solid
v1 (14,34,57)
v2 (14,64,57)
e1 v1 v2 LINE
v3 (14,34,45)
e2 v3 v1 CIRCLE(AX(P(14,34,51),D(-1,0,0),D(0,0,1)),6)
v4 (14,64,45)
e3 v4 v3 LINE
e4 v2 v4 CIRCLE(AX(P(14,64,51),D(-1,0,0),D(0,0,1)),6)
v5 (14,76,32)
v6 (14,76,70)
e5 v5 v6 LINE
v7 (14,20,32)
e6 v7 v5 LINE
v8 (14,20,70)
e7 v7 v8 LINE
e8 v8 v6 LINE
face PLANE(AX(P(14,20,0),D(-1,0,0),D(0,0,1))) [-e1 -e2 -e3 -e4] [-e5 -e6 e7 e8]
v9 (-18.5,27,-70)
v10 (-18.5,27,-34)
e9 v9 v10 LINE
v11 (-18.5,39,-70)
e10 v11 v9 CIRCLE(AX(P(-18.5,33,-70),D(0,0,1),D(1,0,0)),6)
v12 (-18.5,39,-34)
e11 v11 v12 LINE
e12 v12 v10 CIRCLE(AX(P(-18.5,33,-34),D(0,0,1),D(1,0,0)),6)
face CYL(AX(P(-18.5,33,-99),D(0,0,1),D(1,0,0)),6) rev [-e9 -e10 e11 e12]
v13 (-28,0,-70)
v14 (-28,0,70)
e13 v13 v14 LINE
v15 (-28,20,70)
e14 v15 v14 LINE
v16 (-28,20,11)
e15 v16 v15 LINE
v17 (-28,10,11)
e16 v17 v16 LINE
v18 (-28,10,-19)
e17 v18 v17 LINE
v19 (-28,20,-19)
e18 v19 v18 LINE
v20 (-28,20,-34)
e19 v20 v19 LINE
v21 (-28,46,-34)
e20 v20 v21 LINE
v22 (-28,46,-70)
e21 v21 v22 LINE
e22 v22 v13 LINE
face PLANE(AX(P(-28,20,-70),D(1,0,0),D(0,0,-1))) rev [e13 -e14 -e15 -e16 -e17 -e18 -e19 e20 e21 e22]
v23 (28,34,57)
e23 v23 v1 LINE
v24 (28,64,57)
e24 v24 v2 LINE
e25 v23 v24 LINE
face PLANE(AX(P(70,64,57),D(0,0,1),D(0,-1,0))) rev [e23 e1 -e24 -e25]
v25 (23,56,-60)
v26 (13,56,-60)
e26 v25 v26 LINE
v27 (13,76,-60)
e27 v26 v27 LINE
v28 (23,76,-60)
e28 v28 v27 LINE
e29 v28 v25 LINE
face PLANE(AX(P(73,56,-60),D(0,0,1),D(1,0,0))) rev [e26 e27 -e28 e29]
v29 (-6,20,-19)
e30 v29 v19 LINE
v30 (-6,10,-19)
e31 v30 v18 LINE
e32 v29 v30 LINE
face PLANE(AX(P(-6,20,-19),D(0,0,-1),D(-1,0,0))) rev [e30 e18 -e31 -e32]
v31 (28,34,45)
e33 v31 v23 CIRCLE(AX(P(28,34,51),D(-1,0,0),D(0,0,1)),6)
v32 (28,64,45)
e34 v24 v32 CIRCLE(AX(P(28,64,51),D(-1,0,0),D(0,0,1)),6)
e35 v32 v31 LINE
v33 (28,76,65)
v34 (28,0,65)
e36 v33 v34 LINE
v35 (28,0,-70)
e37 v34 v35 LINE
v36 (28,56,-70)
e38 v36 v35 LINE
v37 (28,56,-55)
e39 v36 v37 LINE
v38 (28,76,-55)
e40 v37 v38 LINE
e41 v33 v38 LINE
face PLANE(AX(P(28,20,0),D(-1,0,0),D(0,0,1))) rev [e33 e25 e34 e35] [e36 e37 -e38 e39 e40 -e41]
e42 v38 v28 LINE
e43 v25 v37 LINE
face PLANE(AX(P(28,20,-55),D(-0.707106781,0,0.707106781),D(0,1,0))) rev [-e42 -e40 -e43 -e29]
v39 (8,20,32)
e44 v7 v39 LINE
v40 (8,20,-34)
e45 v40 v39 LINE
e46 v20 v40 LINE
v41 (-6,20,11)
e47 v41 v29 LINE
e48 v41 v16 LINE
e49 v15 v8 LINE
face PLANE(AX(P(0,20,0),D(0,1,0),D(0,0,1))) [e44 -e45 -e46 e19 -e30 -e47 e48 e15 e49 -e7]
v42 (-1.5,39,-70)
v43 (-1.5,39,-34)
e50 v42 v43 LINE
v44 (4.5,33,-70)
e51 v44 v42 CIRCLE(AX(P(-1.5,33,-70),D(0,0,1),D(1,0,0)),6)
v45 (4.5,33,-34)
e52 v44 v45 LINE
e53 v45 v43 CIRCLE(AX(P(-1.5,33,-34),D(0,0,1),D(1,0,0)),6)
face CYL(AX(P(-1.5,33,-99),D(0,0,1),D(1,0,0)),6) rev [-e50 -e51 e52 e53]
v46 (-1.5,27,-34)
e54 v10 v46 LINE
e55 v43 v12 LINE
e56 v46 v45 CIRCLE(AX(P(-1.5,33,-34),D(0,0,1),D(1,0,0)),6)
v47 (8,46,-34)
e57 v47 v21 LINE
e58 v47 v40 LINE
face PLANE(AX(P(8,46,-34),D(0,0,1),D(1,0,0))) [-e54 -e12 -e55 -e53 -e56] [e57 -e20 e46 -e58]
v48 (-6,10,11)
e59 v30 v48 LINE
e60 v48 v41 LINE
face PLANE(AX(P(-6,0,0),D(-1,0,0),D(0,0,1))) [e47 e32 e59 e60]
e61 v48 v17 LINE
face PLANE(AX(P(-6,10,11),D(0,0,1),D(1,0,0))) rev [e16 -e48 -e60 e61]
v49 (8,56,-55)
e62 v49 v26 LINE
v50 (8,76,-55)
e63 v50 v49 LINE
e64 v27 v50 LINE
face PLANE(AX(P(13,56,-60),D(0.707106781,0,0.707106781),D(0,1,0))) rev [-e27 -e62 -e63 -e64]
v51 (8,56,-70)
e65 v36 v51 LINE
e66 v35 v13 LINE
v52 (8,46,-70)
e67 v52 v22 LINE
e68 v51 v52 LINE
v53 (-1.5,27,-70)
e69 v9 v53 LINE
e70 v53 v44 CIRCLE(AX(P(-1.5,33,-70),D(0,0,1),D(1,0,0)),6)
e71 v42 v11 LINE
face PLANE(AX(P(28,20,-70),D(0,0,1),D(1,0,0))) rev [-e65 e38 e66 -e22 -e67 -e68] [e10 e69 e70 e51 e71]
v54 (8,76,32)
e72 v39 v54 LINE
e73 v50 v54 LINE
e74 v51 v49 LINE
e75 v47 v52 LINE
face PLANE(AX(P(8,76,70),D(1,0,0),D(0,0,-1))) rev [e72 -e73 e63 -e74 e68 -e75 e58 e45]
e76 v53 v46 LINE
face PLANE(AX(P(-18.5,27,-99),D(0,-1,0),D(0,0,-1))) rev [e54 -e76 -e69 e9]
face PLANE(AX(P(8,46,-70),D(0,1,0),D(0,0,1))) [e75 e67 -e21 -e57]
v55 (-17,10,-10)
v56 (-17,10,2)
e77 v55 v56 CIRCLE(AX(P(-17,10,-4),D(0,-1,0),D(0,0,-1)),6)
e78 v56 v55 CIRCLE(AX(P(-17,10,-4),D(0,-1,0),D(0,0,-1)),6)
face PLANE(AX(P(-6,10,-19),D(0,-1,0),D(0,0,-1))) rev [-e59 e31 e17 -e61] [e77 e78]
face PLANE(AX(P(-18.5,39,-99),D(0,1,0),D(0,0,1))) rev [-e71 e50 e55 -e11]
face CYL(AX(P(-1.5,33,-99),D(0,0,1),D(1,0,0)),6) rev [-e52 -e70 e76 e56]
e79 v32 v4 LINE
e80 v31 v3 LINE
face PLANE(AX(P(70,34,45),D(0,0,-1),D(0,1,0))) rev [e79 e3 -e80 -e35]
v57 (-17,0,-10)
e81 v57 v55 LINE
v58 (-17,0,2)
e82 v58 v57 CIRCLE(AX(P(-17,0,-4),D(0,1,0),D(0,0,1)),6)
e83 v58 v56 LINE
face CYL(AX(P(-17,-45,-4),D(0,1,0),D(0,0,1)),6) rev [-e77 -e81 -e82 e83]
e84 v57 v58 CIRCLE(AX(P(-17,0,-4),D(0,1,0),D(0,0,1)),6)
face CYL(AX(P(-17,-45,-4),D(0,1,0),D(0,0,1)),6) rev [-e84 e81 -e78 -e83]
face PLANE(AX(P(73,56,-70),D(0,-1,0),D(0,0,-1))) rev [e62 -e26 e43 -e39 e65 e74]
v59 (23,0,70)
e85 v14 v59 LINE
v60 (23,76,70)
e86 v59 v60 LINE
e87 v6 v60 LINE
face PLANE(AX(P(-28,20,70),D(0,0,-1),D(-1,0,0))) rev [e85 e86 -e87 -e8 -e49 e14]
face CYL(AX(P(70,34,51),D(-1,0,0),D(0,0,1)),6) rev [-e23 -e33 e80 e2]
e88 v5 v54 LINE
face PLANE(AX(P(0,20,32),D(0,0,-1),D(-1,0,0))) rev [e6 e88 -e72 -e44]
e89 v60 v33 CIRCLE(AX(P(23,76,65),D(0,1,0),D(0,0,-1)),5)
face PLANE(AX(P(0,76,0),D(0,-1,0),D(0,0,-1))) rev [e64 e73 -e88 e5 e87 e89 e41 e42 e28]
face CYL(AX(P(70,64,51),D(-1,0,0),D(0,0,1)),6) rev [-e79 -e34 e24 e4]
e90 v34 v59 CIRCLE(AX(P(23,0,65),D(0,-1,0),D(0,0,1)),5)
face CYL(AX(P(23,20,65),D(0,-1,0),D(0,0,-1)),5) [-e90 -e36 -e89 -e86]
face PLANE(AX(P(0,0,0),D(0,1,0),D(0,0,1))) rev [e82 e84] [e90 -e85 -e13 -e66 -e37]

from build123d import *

# Parameters (mm, degrees)
BASE_PLATE_DEPTH            = 20
UPRIGHT_WALL_SKETCH_W       = 20
UPRIGHT_WALL_SKETCH_H       = 140
UPRIGHT_WALL_DEPTH          = 56
WALL_PROFILE_CUT_SKETCH_W   = 6
WALL_PROFILE_CUT_SKETCH_H   = 38
WALL_PROFILE_CUT_DEPTH      = 56
WALL_SLOT_DEPTH             = 56
TOP_RIDGE_SKETCH_W          = 36
TOP_RIDGE_SKETCH_H          = 46
TOP_RIDGE_DEPTH             = 36
WALL_NOTCH_SKETCH_W         = 30
WALL_NOTCH_SKETCH_H         = 10
WALL_NOTCH_DEPTH            = 22
ROUND_CUT_SKETCH_R          = 6
ROUND_CUT_DEPTH             = 65
STEP_CUT_SKETCH_W           = 10
STEP_CUT_SKETCH_H           = 20
STEP_CUT_DEPTH              = 65
STEP_CHAMFER_5MM_SIZE       = 5
BASE_EDGE_CHAMFER_5X45_SIZE = 5
CORNER_FILLET_R5_R          = 5
RIDGE_SLOT_DEPTH            = 65


with BuildPart() as part:
    # Base Plate Sketch → Base Plate (new body)
    with BuildSketch(Plane(origin=(0, 0, 0), x_dir=(1, 0, 0), z_dir=(0, 1, 0))):
        Polygon((28, 0), (28, 70), (-28, 70), (-28, -70), (28, -70), align=None)
    extrude(amount=BASE_PLATE_DEPTH)

    # Upright Wall Sketch → Upright Wall (add)
    with BuildSketch(Plane(origin=(0, 20, 0), x_dir=(1, 0, 0), z_dir=(0, 1, 0))):
        with Locations((18, 0)):
            Rectangle(UPRIGHT_WALL_SKETCH_W, UPRIGHT_WALL_SKETCH_H)
    extrude(amount=UPRIGHT_WALL_DEPTH)

    # Wall Profile Cut Sketch → Wall Profile Cut (cut)
    with BuildSketch(Plane(origin=(0, 76, 0), x_dir=(1, 0, 0), z_dir=(0, 1, 0))):
        with Locations((11, -51)):
            Rectangle(WALL_PROFILE_CUT_SKETCH_W, WALL_PROFILE_CUT_SKETCH_H)
    extrude(amount=-WALL_PROFILE_CUT_DEPTH, mode=Mode.SUBTRACT)

    # Wall Slot Sketch → Wall Slot (cut)
    with BuildSketch(Plane.ZY.offset(-14)):
        with BuildLine():
            Line((57, 64), (57, 34))
            ThreePointArc((57, 34), (51, 28), (45, 34))
            Line((45, 34), (45, 64))
            ThreePointArc((45, 64), (51, 70), (57, 64))
        make_face()
    extrude(amount=-WALL_SLOT_DEPTH, mode=Mode.SUBTRACT)

    # Top Ridge Sketch → Top Ridge (add)
    with BuildSketch(Plane.ZY.offset(28)):
        with Locations((-52, 23)):
            Rectangle(TOP_RIDGE_SKETCH_W, TOP_RIDGE_SKETCH_H)
    extrude(amount=-TOP_RIDGE_DEPTH)

    # Wall Notch Sketch → Wall Notch (cut)
    with BuildSketch(Plane.ZY.offset(28)):
        with Locations((-4, 15)):
            Rectangle(WALL_NOTCH_SKETCH_W, WALL_NOTCH_SKETCH_H)
    extrude(amount=-WALL_NOTCH_DEPTH, mode=Mode.SUBTRACT)

    # Round Cut Sketch → Round Cut (cut)
    with BuildSketch(Plane(origin=(0, 20, 0), x_dir=(1, 0, 0), z_dir=(0, 1, 0))):
        with Locations(Location((-17, 4, 0), (0, 0, 270))):
            Circle(ROUND_CUT_SKETCH_R)
    extrude(amount=-ROUND_CUT_DEPTH, mode=Mode.SUBTRACT)

    # Step Cut Sketch → Step Cut (cut)
    with BuildSketch(Plane.ZY.offset(-8)):
        with Locations((-65, 66)):
            Rectangle(STEP_CUT_SKETCH_W, STEP_CUT_SKETCH_H)
    extrude(amount=-STEP_CUT_DEPTH, mode=Mode.SUBTRACT)

    # Step Chamfer 5mm
    step_chamfer_5mm_edges = [part.edges().sort_by_distance(p)[0] for p in [
        (8, 66, -60),
    ]]
    chamfer(step_chamfer_5mm_edges, length=STEP_CHAMFER_5MM_SIZE)

    # Base Edge Chamfer 5x45
    base_edge_chamfer_5x45_edges = [part.edges().sort_by_distance(p)[0] for p in [
        (28, 66, -60),
    ]]
    chamfer(base_edge_chamfer_5x45_edges, length=BASE_EDGE_CHAMFER_5X45_SIZE)

    # Corner Fillet R5
    corner_fillet_r5_edges = [part.edges().sort_by_distance(p)[0] for p in [
        (28, 38, 70),
    ]]
    fillet(corner_fillet_r5_edges, radius=CORNER_FILLET_R5_R)

    # Ridge Slot Sketch → Ridge Slot (cut)
    with BuildSketch(Plane.XY.offset(-34)):
        with BuildLine():
            Line((-18.5, 39), (-1.5, 39))
            ThreePointArc((-1.5, 39), (4.5, 33), (-1.5, 27))
            Line((-1.5, 27), (-18.5, 27))
            ThreePointArc((-18.5, 27), (-24.5, 33), (-18.5, 39))
        make_face()
    extrude(amount=-RIDGE_SLOT_DEPTH, mode=Mode.SUBTRACT)


solid = part.part
